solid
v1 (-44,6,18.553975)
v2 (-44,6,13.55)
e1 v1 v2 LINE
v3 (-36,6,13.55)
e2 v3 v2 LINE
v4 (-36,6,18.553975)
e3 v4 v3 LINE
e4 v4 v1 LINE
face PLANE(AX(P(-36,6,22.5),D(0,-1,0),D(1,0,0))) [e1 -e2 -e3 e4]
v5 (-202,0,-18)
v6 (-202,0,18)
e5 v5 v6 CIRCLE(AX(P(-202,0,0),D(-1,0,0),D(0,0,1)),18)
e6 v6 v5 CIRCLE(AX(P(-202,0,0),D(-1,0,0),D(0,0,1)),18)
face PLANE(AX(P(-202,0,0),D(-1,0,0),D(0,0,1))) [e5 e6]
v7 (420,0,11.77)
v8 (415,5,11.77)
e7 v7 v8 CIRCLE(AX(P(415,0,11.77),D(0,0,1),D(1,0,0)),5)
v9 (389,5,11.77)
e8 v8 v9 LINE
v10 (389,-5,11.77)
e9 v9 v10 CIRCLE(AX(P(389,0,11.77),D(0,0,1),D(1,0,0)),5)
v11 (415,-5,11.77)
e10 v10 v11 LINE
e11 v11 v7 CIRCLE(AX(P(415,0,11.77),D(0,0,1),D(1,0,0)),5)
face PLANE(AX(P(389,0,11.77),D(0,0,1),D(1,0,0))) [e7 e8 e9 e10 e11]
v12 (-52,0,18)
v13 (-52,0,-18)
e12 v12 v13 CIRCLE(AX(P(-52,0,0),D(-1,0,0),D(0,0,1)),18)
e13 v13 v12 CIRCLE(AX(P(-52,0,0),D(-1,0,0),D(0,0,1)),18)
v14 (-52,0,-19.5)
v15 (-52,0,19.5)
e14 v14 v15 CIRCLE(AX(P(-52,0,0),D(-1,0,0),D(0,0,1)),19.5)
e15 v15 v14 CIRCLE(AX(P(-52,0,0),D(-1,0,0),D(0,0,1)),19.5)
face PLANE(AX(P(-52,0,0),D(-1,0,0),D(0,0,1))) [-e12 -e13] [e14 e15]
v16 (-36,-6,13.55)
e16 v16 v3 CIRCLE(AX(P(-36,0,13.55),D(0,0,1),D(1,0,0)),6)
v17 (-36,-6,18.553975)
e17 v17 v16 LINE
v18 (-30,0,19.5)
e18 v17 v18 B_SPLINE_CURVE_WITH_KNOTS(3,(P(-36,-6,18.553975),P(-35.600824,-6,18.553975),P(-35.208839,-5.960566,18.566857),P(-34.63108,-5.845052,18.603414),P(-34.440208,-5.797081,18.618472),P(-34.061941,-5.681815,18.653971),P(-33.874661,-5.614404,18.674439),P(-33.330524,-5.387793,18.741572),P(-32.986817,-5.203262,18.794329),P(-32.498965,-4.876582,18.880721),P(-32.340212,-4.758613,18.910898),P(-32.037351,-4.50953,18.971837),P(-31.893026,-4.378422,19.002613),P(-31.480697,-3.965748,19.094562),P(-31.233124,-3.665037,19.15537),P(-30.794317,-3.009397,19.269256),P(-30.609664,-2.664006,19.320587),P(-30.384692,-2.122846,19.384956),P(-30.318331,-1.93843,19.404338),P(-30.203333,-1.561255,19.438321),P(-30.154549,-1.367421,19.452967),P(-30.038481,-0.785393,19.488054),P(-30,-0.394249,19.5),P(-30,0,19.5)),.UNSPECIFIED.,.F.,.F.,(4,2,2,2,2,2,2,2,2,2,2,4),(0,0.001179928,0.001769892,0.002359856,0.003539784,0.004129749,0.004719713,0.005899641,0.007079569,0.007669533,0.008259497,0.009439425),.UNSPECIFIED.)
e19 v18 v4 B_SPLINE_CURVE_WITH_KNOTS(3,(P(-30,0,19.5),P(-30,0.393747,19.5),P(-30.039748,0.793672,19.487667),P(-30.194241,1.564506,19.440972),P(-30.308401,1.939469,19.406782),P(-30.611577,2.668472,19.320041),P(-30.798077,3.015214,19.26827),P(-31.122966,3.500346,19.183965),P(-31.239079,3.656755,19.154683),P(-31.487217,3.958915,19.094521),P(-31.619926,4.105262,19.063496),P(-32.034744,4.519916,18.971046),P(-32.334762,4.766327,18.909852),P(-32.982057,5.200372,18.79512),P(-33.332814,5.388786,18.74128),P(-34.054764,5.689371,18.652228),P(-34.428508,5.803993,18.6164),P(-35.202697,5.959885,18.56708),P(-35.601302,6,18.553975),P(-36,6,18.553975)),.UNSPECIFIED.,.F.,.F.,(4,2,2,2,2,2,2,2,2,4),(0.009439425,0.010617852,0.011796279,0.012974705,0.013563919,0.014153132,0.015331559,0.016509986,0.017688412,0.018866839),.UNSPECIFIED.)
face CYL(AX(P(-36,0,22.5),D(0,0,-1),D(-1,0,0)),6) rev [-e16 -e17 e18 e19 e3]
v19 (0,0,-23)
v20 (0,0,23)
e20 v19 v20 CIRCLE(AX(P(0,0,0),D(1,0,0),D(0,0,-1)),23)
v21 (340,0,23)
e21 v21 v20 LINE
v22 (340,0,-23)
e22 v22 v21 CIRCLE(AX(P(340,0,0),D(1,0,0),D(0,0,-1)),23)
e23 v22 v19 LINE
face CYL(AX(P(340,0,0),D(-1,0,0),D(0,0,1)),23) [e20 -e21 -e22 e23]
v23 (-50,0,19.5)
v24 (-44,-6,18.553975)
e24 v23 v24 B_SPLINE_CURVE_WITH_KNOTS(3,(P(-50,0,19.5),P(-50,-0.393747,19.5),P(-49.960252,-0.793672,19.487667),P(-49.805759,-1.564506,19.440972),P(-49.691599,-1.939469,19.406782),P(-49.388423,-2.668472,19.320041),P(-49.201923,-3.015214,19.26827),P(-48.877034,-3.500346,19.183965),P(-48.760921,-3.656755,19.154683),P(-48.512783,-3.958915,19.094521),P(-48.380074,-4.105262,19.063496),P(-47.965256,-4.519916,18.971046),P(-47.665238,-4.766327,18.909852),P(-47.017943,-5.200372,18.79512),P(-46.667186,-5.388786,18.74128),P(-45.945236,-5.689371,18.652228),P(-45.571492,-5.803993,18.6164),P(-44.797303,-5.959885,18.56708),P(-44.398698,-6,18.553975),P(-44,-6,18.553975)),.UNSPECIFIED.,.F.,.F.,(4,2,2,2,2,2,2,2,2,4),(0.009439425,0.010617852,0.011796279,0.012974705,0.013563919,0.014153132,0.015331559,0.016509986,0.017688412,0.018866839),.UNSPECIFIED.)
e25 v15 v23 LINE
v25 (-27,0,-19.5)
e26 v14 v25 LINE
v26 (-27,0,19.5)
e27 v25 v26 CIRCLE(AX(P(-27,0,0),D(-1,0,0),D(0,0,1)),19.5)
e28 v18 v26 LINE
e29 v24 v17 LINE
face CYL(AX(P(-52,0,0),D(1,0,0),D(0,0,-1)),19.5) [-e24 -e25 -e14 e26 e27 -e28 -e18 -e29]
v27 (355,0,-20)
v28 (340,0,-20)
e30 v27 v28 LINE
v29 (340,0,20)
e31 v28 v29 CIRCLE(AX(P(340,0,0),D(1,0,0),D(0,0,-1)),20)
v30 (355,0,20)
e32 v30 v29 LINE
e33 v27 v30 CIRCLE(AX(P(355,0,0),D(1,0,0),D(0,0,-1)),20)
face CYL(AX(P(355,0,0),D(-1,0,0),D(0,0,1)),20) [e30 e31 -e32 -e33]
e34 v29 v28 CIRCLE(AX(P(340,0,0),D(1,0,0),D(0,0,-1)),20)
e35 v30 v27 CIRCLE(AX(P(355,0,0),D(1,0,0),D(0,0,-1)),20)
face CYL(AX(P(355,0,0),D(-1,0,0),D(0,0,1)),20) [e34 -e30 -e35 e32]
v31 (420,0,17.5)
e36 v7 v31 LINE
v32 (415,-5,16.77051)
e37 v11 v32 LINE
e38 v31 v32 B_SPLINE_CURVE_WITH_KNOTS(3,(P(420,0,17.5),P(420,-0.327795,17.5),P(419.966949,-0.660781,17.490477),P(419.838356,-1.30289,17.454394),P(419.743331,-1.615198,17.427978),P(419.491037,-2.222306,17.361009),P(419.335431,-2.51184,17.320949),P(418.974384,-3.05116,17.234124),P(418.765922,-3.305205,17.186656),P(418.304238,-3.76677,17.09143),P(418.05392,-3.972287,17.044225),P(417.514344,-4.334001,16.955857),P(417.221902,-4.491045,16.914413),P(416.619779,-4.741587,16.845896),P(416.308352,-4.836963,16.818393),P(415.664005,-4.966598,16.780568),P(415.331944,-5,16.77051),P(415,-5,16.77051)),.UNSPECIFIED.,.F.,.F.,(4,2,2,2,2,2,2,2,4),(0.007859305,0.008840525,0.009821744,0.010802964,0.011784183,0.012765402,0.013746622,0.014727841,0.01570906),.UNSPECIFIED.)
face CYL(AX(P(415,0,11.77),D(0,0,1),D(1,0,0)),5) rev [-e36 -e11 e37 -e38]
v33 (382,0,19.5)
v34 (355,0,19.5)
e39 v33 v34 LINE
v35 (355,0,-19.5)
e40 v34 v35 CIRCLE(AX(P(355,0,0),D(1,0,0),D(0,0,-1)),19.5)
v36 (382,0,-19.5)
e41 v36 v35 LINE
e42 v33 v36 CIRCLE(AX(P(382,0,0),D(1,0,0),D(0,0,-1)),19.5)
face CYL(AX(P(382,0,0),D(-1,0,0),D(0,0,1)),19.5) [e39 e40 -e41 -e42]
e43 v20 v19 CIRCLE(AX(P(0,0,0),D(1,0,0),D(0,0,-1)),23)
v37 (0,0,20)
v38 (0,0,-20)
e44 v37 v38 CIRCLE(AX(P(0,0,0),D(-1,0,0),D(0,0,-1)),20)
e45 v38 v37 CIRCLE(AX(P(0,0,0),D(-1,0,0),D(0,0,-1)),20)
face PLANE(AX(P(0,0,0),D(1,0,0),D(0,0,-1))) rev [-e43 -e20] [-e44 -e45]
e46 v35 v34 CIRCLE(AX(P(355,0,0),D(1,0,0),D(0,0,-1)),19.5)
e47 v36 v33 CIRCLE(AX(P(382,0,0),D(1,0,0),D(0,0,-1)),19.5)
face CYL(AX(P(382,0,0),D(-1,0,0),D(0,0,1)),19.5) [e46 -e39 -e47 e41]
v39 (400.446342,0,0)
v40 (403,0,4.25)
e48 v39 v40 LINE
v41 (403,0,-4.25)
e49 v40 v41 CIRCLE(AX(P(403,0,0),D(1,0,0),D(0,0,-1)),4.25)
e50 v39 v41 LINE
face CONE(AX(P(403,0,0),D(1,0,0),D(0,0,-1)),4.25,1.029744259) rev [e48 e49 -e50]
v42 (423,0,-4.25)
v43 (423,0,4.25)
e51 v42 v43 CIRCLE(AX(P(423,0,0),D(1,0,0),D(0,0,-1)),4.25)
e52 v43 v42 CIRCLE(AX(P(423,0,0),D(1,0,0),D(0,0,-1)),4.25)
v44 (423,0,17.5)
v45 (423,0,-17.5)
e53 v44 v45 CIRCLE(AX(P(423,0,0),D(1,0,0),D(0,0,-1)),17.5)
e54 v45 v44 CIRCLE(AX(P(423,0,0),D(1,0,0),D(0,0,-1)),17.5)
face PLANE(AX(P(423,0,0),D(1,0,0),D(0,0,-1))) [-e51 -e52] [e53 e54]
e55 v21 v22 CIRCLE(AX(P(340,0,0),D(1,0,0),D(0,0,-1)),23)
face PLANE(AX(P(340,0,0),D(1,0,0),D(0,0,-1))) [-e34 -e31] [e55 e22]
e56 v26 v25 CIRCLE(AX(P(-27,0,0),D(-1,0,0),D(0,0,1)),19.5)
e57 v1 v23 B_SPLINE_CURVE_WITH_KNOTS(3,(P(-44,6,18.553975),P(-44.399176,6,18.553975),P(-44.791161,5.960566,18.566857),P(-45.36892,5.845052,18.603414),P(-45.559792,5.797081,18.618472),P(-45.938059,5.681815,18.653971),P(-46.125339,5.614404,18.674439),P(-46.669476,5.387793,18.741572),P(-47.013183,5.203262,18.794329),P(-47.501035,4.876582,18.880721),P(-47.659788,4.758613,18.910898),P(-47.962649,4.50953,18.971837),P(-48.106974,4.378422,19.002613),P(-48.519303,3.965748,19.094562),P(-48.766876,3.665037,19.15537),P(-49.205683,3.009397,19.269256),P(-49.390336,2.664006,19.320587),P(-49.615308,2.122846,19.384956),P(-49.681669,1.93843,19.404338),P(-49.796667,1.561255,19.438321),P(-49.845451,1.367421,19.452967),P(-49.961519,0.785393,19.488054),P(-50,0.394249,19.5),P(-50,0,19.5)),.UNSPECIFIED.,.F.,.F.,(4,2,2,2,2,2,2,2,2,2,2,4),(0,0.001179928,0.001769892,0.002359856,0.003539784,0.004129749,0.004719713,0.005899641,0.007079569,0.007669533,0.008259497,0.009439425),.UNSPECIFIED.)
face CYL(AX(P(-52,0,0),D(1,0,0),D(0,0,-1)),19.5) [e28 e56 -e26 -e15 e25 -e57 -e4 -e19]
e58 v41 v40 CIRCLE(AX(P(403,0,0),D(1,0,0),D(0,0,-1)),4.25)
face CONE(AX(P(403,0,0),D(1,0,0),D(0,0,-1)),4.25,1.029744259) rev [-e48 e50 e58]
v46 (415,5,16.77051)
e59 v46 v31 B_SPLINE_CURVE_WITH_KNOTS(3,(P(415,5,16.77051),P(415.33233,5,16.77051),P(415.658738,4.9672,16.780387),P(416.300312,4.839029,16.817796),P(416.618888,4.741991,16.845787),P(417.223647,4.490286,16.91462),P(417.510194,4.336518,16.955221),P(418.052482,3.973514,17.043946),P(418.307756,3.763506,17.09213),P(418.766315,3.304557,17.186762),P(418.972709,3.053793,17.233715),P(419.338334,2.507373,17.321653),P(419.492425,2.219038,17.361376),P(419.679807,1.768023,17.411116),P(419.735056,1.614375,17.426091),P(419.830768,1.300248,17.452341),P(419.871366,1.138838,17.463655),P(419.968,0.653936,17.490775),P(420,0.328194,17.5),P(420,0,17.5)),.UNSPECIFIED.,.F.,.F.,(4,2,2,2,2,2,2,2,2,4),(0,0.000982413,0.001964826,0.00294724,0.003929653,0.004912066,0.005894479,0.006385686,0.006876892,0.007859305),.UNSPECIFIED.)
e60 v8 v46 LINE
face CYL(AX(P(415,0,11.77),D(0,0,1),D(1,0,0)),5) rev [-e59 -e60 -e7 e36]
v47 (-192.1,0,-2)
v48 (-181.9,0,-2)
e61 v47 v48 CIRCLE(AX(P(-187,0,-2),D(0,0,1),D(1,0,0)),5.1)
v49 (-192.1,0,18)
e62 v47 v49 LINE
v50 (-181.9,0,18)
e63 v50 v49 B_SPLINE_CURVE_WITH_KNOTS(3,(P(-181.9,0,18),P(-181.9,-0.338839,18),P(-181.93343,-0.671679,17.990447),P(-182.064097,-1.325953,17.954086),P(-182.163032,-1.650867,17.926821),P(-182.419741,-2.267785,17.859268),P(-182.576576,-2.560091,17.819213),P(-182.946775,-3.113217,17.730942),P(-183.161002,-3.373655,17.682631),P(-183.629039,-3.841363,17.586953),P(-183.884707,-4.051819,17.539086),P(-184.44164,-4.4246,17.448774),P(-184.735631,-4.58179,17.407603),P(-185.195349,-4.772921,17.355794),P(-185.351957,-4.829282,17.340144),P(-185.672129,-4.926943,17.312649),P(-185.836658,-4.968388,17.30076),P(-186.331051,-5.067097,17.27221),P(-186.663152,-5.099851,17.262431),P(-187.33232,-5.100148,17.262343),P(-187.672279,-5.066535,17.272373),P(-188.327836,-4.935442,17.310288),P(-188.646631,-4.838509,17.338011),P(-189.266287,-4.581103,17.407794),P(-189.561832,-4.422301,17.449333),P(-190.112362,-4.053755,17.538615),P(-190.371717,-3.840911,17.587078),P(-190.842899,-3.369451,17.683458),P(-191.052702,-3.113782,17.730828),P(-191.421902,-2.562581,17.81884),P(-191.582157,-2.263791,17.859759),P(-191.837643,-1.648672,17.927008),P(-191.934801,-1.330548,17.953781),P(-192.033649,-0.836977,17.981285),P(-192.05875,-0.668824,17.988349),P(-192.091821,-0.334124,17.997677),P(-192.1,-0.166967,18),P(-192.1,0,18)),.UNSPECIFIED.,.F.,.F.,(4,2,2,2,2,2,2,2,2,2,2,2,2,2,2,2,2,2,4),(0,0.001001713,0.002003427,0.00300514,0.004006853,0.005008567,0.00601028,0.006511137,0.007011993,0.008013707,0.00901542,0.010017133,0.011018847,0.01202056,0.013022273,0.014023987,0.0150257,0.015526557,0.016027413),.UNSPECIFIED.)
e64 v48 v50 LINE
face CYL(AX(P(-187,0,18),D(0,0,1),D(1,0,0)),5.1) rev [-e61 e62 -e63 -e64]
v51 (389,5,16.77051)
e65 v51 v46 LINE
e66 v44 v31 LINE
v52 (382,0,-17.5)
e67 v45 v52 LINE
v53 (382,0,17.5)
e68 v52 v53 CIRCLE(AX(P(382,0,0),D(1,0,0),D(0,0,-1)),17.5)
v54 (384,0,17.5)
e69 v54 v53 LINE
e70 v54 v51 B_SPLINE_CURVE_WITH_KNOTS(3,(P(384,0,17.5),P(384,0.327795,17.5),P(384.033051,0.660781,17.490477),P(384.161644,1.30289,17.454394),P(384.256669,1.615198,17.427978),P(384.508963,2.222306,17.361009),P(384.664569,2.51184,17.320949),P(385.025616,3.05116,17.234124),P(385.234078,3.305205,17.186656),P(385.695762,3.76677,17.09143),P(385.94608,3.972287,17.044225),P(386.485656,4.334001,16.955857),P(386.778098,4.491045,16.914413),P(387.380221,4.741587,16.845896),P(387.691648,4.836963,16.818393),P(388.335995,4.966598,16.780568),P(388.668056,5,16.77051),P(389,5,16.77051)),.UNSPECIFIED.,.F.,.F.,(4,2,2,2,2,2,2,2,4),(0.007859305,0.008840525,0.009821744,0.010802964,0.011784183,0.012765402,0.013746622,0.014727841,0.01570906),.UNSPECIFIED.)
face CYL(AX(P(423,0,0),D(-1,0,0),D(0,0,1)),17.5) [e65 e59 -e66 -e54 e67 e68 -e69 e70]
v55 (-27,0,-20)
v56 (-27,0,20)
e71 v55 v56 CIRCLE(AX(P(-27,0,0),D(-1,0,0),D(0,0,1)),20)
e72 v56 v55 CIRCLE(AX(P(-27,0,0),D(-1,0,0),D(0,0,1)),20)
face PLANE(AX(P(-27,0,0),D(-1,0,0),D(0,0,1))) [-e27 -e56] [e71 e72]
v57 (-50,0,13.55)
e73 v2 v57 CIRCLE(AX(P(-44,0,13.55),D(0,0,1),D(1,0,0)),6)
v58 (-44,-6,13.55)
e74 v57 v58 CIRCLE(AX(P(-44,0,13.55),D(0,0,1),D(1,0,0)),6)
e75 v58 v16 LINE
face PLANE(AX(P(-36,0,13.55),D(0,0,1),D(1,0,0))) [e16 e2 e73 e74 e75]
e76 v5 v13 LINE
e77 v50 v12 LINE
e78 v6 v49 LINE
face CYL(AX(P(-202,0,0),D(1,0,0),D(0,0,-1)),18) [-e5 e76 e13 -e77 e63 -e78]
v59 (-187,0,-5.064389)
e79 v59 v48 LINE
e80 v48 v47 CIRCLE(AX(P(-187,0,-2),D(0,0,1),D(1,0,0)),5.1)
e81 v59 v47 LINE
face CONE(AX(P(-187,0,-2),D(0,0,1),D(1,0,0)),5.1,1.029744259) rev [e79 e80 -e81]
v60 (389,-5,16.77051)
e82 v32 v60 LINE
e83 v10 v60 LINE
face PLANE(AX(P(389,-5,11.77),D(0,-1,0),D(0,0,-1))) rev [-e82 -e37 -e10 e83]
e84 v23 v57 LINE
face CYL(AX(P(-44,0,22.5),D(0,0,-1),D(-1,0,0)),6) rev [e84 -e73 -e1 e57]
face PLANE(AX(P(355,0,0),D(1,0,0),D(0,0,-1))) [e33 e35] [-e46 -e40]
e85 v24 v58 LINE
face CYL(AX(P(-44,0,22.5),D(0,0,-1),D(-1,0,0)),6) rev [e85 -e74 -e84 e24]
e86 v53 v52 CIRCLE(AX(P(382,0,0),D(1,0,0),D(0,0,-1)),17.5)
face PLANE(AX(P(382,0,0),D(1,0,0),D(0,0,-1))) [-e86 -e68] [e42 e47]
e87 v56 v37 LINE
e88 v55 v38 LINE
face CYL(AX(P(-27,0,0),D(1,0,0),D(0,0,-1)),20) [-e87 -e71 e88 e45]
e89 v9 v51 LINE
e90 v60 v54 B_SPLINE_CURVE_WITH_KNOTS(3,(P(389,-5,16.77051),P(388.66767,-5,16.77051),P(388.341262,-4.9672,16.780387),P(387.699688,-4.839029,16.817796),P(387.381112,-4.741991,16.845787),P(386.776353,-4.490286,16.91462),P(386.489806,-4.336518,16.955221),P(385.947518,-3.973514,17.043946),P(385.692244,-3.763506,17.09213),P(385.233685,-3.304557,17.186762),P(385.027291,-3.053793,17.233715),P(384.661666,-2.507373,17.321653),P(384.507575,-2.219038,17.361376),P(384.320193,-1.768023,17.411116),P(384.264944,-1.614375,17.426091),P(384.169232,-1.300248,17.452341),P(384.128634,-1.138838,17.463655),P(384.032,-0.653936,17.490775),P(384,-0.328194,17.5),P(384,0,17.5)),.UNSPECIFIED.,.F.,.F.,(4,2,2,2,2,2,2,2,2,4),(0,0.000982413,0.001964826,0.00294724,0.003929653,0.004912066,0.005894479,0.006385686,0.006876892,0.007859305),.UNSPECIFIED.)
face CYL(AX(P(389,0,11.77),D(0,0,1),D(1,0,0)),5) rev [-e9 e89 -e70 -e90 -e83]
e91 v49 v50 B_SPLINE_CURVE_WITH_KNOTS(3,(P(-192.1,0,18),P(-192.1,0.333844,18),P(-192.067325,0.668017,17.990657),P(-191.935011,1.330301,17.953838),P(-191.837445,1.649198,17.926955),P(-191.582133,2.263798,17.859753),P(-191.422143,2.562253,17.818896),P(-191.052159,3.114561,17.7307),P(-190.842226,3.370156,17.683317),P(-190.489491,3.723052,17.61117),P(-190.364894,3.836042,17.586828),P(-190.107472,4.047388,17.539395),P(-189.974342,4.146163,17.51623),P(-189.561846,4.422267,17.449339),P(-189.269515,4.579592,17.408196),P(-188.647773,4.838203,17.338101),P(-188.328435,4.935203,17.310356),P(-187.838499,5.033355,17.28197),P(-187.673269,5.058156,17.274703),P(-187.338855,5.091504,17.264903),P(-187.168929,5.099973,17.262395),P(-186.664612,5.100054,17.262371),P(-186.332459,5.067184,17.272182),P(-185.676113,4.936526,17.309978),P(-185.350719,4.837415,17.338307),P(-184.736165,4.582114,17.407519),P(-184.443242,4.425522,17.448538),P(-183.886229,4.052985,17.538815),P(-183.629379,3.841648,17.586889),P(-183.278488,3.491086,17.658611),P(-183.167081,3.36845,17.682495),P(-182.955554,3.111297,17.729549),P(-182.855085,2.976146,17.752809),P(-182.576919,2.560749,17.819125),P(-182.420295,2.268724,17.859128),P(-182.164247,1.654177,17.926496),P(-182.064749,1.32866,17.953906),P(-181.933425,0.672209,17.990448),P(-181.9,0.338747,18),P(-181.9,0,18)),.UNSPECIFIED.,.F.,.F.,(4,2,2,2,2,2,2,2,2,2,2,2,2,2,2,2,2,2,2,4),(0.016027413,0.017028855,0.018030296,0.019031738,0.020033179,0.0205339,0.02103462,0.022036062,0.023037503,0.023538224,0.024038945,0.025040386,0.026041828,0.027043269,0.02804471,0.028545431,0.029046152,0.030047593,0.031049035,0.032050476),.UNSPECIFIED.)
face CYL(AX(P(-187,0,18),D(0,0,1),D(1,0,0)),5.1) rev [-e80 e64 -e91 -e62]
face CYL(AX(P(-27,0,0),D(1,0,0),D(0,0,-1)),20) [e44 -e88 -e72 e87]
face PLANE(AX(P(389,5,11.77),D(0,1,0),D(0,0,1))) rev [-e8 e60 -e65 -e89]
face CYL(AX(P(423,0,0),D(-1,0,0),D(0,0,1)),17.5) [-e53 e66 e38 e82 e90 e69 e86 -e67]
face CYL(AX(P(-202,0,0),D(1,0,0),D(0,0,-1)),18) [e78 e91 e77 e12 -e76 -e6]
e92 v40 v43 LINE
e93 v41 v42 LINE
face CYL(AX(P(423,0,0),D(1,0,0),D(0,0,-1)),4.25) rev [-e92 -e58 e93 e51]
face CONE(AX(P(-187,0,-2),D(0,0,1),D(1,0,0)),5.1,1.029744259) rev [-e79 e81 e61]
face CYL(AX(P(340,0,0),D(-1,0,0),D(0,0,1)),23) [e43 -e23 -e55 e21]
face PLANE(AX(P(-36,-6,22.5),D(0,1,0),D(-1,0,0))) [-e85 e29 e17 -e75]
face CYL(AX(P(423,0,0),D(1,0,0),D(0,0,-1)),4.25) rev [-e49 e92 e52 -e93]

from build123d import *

# Parameters (mm, degrees)
SKETCH_1_R               = 23
EXTRUDE_1_DEPTH          = 340
SKETCH_2_R               = 20
EXTRUDE_2_DEPTH          = 27
SKETCH_3_R               = 19.5
EXTRUDE_3_DEPTH          = 25
EXTRUDE_START            = 15
SKETCH_4_R               = 20
EXTRUDE_4_DEPTH          = 15
EXTRUDE_START_2          = 27
SKETCH_5_R               = 19.5
EXTRUDE_5_DEPTH          = 27
SKETCH_6_R               = 17.5
EXTRUDE_6_DEPTH          = 41
CUT_EXTRUDE_1_DEPTH      = 5.73
SKETCH_8_R               = 18
EXTRUDE_7_DEPTH          = 150
HOLE_WIZARD_M12_2_D      = 10.2
HOLE_WIZARD_M12_2_DEPTH  = 20
HOLE_WIZARD_M12_2_TIP    = 3.064389157
HOLE_WIZARD_M10_1_D      = 8.5
HOLE_WIZARD_M10_1_DEPTH  = 20
HOLE_WIZARD_M10_1_TIP    = 2.553657631
CUT_EXTRUDE_2_DEPTH      = 5
CUT_EXTRUDE_2_DEPTH_BACK = 3.95


with BuildPart() as part:
    # 草图1 → 凸台-拉伸1 (new body)
    with BuildSketch(Plane(origin=(0, 0, 0), x_dir=(0, 0, -1), z_dir=(1, 0, 0))):
        Circle(SKETCH_1_R)
    extrude(amount=EXTRUDE_1_DEPTH)

    # 草图2 → 凸台-拉伸2 (add)
    with BuildSketch(Plane.ZY):
        with Locations(Location((0, 0, 0), (0, 0, 180))):
            Circle(SKETCH_2_R)
    extrude(amount=EXTRUDE_2_DEPTH)

    # 草图3 → 凸台-拉伸3 (add)
    with BuildSketch(Plane.ZY.offset(27)):
        Circle(SKETCH_3_R)
    extrude(amount=EXTRUDE_3_DEPTH)

    # 草图4 → 凸台-拉伸4 (add)
    with BuildSketch(Plane(origin=(340, 0, 0), x_dir=(0, 0, -1), z_dir=(1, 0, 0)).offset(EXTRUDE_START)):
        Circle(SKETCH_4_R)
    extrude(amount=-EXTRUDE_4_DEPTH)

    # 草图5 → 凸台-拉伸5 (add)
    with BuildSketch(Plane(origin=(355, 0, 0), x_dir=(0, 0, -1), z_dir=(1, 0, 0)).offset(EXTRUDE_START_2)):
        with Locations(Location((0, 0, 0), (0, 0, 180))):
            Circle(SKETCH_5_R)
    extrude(amount=-EXTRUDE_5_DEPTH)

    # 草图6 → 凸台-拉伸6 (add)
    with BuildSketch(Plane(origin=(382, 0, 0), x_dir=(0, 0, -1), z_dir=(1, 0, 0))):
        Circle(SKETCH_6_R)
    extrude(amount=EXTRUDE_6_DEPTH)

    # 草图7 → 切除-拉伸1 (cut)
    with BuildSketch(Plane.XY.offset(17.5)):
        with BuildLine():
            Line((389, 5), (415, 5))
            ThreePointArc((415, 5), (420, 0), (415, -5))
            Line((415, -5), (389, -5))
            ThreePointArc((389, -5), (384, 0), (389, 5))
        make_face()
    extrude(amount=-CUT_EXTRUDE_1_DEPTH, mode=Mode.SUBTRACT)

    # 草图8 → 凸台-拉伸7 (add)
    with BuildSketch(Plane.ZY.offset(52)):
        Circle(SKETCH_8_R)
    extrude(amount=EXTRUDE_7_DEPTH)

    # M12 螺纹孔2
    with Locations(Plane.XY.offset(18)):
        with Locations((-187, 0)):
            Hole(HOLE_WIZARD_M12_2_D / 2, depth=HOLE_WIZARD_M12_2_DEPTH)
            with Locations((0, 0, -(HOLE_WIZARD_M12_2_DEPTH + HOLE_WIZARD_M12_2_TIP / 2))):  # 118° drill point
                Cone(0, HOLE_WIZARD_M12_2_D / 2, HOLE_WIZARD_M12_2_TIP, mode=Mode.SUBTRACT)

    # M10 螺纹孔1
    with Locations(Plane(origin=(423, 0, 0), x_dir=(0, 0, -1), z_dir=(1, 0, 0))):
        with Locations((0, 0)):
            Hole(HOLE_WIZARD_M10_1_D / 2, depth=HOLE_WIZARD_M10_1_DEPTH)
            with Locations((0, 0, -(HOLE_WIZARD_M10_1_DEPTH + HOLE_WIZARD_M10_1_TIP / 2))):  # 118° drill point
                Cone(0, HOLE_WIZARD_M10_1_D / 2, HOLE_WIZARD_M10_1_TIP, mode=Mode.SUBTRACT)

    # 草图18 → 切除-拉伸2 (cut, two sides: drawn at the far end of the back side and taken through both)
    with BuildSketch(Plane.XY.offset(17.5).offset(-CUT_EXTRUDE_2_DEPTH_BACK)):
        with BuildLine():
            Line((-36, -6), (-44, -6))
            ThreePointArc((-44, -6), (-50, 0), (-44, 6))
            Line((-44, 6), (-36, 6))
            ThreePointArc((-36, 6), (-30, 0), (-36, -6))
        make_face()
    extrude(amount=CUT_EXTRUDE_2_DEPTH + CUT_EXTRUDE_2_DEPTH_BACK, mode=Mode.SUBTRACT)


solid = part.part
